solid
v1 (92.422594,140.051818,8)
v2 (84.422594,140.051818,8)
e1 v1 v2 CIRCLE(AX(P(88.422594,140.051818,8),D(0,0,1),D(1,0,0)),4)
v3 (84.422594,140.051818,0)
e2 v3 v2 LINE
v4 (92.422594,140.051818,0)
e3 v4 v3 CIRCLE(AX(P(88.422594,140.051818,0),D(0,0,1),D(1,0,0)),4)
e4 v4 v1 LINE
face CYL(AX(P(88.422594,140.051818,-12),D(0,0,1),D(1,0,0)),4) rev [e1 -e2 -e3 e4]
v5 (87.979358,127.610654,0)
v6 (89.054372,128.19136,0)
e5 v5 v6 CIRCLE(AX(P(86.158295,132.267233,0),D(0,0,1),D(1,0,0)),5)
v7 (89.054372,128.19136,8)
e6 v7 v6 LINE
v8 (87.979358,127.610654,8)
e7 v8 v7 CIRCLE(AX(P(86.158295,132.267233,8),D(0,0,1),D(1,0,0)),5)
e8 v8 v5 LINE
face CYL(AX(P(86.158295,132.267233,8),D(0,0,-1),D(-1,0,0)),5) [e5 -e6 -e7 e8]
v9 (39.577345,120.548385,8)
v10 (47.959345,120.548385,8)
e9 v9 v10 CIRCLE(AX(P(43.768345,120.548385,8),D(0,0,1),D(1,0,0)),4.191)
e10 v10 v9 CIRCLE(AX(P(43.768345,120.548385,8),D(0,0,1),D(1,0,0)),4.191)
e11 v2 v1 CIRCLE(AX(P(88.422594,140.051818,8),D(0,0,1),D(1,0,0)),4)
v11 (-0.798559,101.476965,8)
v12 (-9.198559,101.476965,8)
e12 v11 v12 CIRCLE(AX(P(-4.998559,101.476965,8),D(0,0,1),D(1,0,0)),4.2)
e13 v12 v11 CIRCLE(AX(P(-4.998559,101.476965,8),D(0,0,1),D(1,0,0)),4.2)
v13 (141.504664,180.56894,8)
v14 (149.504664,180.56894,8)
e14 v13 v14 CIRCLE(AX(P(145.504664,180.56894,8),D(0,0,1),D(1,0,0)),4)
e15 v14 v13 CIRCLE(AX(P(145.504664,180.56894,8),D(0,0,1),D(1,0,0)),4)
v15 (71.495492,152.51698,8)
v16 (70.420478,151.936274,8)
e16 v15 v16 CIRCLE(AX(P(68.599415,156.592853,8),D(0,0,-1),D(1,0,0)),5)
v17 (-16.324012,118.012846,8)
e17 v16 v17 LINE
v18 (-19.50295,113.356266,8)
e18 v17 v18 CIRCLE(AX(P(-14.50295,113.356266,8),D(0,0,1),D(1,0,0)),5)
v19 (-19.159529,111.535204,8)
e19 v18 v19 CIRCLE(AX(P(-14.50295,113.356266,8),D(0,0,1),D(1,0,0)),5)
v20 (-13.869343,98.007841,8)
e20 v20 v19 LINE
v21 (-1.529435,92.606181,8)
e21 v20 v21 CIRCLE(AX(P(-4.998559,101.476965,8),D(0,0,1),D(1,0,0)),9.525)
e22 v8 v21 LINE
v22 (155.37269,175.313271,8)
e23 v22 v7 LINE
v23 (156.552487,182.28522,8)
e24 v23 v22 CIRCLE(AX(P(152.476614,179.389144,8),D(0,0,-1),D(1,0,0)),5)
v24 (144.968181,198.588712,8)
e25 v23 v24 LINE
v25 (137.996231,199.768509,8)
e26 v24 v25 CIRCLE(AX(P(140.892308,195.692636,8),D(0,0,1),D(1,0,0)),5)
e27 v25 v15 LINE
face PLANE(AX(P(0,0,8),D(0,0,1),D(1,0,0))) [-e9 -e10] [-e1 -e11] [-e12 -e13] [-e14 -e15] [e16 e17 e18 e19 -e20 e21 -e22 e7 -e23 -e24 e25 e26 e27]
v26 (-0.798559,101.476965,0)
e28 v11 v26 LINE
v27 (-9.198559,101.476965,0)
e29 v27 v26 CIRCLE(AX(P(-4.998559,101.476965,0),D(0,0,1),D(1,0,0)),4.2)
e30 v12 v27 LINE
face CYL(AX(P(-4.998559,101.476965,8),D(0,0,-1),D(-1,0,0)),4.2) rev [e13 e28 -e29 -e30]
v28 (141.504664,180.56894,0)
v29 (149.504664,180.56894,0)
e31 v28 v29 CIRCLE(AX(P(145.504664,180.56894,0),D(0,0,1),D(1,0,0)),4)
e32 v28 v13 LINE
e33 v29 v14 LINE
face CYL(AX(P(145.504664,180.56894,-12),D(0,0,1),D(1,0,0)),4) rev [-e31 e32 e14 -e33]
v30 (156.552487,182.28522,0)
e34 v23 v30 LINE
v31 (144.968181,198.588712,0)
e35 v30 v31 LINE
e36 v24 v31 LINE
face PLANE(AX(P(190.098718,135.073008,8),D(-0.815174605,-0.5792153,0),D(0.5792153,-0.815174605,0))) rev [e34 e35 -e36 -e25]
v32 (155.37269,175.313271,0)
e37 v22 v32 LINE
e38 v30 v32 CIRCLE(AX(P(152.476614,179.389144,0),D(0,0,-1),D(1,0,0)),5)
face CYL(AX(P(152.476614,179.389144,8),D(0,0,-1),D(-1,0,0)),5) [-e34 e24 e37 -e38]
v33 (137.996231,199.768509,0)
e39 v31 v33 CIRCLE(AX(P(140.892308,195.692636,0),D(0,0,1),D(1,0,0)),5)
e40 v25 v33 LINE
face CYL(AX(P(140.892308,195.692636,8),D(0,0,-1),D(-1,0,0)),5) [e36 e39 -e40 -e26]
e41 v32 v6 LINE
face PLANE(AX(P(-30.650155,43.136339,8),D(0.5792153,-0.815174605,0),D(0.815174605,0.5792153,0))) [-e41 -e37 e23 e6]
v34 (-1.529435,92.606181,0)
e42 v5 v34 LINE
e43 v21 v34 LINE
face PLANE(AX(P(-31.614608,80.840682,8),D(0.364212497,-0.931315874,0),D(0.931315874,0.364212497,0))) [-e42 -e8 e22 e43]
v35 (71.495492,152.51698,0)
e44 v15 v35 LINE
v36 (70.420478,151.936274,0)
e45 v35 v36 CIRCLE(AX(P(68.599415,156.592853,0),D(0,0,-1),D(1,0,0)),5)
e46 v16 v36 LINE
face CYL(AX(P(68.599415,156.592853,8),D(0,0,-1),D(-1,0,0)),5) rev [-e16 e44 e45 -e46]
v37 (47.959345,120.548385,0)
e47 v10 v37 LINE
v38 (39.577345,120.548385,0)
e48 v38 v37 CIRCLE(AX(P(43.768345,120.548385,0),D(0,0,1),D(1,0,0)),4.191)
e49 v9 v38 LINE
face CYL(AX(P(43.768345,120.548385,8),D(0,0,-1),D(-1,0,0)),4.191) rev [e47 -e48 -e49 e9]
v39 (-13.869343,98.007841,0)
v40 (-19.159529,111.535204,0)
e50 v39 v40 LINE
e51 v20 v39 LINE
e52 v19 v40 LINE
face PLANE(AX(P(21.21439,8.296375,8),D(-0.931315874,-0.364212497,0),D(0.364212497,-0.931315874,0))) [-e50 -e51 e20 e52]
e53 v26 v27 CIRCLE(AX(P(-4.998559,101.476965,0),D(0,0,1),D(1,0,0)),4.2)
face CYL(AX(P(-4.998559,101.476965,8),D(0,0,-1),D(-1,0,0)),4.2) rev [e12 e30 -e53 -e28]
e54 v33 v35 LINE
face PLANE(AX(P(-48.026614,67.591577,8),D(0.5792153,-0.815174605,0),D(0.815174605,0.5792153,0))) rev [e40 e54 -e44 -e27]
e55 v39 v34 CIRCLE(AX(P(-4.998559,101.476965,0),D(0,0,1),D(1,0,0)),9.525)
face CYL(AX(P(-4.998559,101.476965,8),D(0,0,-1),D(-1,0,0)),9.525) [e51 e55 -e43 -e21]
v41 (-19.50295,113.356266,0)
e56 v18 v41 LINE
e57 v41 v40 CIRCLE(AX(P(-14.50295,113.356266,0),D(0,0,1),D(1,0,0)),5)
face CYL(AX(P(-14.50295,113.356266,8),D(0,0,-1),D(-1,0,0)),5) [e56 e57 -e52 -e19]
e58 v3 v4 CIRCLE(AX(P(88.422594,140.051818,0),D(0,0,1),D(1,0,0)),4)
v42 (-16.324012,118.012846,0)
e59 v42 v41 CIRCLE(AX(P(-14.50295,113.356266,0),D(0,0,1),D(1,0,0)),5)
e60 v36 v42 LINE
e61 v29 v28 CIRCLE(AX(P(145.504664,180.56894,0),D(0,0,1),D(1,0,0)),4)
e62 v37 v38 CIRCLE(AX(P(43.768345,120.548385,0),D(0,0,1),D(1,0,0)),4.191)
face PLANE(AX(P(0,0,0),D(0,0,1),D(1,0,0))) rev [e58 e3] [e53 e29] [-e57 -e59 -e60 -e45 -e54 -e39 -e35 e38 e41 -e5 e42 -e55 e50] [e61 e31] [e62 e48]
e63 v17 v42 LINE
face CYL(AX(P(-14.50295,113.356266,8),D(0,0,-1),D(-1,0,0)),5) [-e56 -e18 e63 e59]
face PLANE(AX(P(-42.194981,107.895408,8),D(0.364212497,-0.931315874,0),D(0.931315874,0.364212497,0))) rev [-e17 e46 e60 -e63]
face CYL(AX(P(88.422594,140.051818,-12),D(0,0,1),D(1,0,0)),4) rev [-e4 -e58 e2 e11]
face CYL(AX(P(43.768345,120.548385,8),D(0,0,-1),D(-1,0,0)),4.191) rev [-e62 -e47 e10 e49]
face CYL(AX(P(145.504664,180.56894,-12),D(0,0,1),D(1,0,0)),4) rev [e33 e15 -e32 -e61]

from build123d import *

# Parameters (mm, degrees)
SKETCH_1_R          = 4.191
SKETCH_1_R_2        = 4.2
EXTRUDE_1_DEPTH     = 8
SKETCH_2_R          = 4
CUT_EXTRUDE_1_DEPTH = 20


with BuildPart() as part:
    # 草图1 → 凸台-拉伸1 (new body)
    with BuildSketch(Plane.XY):
        with BuildLine():
            Line((87.979357684, 127.610653672), (-1.529435027, 92.60618121))
            ThreePointArc((-1.529435027, 92.60618121), (-8.81810924, 92.751332474), (-13.869342758, 98.007840879))
            Line((-13.869342758, 98.007840879), (-19.159529273, 111.53520395))
            ThreePointArc((-19.159529273, 111.53520395), (-19.083334383, 115.361279652), (-16.324012386, 118.012845804))
            Line((-16.324012386, 118.012845804), (70.420477634, 151.936274108))
            ThreePointArc((70.420477634, 151.936274108), (70.975789492, 152.193666623), (71.49549165, 152.516980454))
            Line((71.49549165, 152.516980454), (137.996231332, 199.768508694))
            ThreePointArc((137.996231332, 199.768508694), (141.726549955, 200.622548455), (144.968180855, 198.588712168))
            Line((144.968180855, 198.588712168), (156.55248685, 182.285220069))
            ThreePointArc((156.55248685, 182.285220069), (157.406526611, 178.554901446), (155.372690324, 175.313270545))
            Line((155.372690324, 175.313270545), (89.054371699, 128.191360017))
            ThreePointArc((89.054371699, 128.191360017), (88.534669542, 127.868046187), (87.979357684, 127.610653672))
        make_face()
        with Locations((43.76834518, 120.548384653)):
            Circle(SKETCH_1_R, mode=Mode.SUBTRACT)
        with Locations((-4.998559058, 101.47696491)):
            Circle(SKETCH_1_R_2, mode=Mode.SUBTRACT)
    extrude(amount=EXTRUDE_1_DEPTH)

    # 草图2 → 切除-拉伸1 (cut)
    with BuildSketch(Plane.XY.offset(8)):
        with Locations((145.504664302, 180.568940096)):
            Circle(SKETCH_2_R)
        with Locations((88.422593517, 140.051817853)):
            Circle(SKETCH_2_R)
    extrude(amount=-CUT_EXTRUDE_1_DEPTH, mode=Mode.SUBTRACT)


solid = part.part
